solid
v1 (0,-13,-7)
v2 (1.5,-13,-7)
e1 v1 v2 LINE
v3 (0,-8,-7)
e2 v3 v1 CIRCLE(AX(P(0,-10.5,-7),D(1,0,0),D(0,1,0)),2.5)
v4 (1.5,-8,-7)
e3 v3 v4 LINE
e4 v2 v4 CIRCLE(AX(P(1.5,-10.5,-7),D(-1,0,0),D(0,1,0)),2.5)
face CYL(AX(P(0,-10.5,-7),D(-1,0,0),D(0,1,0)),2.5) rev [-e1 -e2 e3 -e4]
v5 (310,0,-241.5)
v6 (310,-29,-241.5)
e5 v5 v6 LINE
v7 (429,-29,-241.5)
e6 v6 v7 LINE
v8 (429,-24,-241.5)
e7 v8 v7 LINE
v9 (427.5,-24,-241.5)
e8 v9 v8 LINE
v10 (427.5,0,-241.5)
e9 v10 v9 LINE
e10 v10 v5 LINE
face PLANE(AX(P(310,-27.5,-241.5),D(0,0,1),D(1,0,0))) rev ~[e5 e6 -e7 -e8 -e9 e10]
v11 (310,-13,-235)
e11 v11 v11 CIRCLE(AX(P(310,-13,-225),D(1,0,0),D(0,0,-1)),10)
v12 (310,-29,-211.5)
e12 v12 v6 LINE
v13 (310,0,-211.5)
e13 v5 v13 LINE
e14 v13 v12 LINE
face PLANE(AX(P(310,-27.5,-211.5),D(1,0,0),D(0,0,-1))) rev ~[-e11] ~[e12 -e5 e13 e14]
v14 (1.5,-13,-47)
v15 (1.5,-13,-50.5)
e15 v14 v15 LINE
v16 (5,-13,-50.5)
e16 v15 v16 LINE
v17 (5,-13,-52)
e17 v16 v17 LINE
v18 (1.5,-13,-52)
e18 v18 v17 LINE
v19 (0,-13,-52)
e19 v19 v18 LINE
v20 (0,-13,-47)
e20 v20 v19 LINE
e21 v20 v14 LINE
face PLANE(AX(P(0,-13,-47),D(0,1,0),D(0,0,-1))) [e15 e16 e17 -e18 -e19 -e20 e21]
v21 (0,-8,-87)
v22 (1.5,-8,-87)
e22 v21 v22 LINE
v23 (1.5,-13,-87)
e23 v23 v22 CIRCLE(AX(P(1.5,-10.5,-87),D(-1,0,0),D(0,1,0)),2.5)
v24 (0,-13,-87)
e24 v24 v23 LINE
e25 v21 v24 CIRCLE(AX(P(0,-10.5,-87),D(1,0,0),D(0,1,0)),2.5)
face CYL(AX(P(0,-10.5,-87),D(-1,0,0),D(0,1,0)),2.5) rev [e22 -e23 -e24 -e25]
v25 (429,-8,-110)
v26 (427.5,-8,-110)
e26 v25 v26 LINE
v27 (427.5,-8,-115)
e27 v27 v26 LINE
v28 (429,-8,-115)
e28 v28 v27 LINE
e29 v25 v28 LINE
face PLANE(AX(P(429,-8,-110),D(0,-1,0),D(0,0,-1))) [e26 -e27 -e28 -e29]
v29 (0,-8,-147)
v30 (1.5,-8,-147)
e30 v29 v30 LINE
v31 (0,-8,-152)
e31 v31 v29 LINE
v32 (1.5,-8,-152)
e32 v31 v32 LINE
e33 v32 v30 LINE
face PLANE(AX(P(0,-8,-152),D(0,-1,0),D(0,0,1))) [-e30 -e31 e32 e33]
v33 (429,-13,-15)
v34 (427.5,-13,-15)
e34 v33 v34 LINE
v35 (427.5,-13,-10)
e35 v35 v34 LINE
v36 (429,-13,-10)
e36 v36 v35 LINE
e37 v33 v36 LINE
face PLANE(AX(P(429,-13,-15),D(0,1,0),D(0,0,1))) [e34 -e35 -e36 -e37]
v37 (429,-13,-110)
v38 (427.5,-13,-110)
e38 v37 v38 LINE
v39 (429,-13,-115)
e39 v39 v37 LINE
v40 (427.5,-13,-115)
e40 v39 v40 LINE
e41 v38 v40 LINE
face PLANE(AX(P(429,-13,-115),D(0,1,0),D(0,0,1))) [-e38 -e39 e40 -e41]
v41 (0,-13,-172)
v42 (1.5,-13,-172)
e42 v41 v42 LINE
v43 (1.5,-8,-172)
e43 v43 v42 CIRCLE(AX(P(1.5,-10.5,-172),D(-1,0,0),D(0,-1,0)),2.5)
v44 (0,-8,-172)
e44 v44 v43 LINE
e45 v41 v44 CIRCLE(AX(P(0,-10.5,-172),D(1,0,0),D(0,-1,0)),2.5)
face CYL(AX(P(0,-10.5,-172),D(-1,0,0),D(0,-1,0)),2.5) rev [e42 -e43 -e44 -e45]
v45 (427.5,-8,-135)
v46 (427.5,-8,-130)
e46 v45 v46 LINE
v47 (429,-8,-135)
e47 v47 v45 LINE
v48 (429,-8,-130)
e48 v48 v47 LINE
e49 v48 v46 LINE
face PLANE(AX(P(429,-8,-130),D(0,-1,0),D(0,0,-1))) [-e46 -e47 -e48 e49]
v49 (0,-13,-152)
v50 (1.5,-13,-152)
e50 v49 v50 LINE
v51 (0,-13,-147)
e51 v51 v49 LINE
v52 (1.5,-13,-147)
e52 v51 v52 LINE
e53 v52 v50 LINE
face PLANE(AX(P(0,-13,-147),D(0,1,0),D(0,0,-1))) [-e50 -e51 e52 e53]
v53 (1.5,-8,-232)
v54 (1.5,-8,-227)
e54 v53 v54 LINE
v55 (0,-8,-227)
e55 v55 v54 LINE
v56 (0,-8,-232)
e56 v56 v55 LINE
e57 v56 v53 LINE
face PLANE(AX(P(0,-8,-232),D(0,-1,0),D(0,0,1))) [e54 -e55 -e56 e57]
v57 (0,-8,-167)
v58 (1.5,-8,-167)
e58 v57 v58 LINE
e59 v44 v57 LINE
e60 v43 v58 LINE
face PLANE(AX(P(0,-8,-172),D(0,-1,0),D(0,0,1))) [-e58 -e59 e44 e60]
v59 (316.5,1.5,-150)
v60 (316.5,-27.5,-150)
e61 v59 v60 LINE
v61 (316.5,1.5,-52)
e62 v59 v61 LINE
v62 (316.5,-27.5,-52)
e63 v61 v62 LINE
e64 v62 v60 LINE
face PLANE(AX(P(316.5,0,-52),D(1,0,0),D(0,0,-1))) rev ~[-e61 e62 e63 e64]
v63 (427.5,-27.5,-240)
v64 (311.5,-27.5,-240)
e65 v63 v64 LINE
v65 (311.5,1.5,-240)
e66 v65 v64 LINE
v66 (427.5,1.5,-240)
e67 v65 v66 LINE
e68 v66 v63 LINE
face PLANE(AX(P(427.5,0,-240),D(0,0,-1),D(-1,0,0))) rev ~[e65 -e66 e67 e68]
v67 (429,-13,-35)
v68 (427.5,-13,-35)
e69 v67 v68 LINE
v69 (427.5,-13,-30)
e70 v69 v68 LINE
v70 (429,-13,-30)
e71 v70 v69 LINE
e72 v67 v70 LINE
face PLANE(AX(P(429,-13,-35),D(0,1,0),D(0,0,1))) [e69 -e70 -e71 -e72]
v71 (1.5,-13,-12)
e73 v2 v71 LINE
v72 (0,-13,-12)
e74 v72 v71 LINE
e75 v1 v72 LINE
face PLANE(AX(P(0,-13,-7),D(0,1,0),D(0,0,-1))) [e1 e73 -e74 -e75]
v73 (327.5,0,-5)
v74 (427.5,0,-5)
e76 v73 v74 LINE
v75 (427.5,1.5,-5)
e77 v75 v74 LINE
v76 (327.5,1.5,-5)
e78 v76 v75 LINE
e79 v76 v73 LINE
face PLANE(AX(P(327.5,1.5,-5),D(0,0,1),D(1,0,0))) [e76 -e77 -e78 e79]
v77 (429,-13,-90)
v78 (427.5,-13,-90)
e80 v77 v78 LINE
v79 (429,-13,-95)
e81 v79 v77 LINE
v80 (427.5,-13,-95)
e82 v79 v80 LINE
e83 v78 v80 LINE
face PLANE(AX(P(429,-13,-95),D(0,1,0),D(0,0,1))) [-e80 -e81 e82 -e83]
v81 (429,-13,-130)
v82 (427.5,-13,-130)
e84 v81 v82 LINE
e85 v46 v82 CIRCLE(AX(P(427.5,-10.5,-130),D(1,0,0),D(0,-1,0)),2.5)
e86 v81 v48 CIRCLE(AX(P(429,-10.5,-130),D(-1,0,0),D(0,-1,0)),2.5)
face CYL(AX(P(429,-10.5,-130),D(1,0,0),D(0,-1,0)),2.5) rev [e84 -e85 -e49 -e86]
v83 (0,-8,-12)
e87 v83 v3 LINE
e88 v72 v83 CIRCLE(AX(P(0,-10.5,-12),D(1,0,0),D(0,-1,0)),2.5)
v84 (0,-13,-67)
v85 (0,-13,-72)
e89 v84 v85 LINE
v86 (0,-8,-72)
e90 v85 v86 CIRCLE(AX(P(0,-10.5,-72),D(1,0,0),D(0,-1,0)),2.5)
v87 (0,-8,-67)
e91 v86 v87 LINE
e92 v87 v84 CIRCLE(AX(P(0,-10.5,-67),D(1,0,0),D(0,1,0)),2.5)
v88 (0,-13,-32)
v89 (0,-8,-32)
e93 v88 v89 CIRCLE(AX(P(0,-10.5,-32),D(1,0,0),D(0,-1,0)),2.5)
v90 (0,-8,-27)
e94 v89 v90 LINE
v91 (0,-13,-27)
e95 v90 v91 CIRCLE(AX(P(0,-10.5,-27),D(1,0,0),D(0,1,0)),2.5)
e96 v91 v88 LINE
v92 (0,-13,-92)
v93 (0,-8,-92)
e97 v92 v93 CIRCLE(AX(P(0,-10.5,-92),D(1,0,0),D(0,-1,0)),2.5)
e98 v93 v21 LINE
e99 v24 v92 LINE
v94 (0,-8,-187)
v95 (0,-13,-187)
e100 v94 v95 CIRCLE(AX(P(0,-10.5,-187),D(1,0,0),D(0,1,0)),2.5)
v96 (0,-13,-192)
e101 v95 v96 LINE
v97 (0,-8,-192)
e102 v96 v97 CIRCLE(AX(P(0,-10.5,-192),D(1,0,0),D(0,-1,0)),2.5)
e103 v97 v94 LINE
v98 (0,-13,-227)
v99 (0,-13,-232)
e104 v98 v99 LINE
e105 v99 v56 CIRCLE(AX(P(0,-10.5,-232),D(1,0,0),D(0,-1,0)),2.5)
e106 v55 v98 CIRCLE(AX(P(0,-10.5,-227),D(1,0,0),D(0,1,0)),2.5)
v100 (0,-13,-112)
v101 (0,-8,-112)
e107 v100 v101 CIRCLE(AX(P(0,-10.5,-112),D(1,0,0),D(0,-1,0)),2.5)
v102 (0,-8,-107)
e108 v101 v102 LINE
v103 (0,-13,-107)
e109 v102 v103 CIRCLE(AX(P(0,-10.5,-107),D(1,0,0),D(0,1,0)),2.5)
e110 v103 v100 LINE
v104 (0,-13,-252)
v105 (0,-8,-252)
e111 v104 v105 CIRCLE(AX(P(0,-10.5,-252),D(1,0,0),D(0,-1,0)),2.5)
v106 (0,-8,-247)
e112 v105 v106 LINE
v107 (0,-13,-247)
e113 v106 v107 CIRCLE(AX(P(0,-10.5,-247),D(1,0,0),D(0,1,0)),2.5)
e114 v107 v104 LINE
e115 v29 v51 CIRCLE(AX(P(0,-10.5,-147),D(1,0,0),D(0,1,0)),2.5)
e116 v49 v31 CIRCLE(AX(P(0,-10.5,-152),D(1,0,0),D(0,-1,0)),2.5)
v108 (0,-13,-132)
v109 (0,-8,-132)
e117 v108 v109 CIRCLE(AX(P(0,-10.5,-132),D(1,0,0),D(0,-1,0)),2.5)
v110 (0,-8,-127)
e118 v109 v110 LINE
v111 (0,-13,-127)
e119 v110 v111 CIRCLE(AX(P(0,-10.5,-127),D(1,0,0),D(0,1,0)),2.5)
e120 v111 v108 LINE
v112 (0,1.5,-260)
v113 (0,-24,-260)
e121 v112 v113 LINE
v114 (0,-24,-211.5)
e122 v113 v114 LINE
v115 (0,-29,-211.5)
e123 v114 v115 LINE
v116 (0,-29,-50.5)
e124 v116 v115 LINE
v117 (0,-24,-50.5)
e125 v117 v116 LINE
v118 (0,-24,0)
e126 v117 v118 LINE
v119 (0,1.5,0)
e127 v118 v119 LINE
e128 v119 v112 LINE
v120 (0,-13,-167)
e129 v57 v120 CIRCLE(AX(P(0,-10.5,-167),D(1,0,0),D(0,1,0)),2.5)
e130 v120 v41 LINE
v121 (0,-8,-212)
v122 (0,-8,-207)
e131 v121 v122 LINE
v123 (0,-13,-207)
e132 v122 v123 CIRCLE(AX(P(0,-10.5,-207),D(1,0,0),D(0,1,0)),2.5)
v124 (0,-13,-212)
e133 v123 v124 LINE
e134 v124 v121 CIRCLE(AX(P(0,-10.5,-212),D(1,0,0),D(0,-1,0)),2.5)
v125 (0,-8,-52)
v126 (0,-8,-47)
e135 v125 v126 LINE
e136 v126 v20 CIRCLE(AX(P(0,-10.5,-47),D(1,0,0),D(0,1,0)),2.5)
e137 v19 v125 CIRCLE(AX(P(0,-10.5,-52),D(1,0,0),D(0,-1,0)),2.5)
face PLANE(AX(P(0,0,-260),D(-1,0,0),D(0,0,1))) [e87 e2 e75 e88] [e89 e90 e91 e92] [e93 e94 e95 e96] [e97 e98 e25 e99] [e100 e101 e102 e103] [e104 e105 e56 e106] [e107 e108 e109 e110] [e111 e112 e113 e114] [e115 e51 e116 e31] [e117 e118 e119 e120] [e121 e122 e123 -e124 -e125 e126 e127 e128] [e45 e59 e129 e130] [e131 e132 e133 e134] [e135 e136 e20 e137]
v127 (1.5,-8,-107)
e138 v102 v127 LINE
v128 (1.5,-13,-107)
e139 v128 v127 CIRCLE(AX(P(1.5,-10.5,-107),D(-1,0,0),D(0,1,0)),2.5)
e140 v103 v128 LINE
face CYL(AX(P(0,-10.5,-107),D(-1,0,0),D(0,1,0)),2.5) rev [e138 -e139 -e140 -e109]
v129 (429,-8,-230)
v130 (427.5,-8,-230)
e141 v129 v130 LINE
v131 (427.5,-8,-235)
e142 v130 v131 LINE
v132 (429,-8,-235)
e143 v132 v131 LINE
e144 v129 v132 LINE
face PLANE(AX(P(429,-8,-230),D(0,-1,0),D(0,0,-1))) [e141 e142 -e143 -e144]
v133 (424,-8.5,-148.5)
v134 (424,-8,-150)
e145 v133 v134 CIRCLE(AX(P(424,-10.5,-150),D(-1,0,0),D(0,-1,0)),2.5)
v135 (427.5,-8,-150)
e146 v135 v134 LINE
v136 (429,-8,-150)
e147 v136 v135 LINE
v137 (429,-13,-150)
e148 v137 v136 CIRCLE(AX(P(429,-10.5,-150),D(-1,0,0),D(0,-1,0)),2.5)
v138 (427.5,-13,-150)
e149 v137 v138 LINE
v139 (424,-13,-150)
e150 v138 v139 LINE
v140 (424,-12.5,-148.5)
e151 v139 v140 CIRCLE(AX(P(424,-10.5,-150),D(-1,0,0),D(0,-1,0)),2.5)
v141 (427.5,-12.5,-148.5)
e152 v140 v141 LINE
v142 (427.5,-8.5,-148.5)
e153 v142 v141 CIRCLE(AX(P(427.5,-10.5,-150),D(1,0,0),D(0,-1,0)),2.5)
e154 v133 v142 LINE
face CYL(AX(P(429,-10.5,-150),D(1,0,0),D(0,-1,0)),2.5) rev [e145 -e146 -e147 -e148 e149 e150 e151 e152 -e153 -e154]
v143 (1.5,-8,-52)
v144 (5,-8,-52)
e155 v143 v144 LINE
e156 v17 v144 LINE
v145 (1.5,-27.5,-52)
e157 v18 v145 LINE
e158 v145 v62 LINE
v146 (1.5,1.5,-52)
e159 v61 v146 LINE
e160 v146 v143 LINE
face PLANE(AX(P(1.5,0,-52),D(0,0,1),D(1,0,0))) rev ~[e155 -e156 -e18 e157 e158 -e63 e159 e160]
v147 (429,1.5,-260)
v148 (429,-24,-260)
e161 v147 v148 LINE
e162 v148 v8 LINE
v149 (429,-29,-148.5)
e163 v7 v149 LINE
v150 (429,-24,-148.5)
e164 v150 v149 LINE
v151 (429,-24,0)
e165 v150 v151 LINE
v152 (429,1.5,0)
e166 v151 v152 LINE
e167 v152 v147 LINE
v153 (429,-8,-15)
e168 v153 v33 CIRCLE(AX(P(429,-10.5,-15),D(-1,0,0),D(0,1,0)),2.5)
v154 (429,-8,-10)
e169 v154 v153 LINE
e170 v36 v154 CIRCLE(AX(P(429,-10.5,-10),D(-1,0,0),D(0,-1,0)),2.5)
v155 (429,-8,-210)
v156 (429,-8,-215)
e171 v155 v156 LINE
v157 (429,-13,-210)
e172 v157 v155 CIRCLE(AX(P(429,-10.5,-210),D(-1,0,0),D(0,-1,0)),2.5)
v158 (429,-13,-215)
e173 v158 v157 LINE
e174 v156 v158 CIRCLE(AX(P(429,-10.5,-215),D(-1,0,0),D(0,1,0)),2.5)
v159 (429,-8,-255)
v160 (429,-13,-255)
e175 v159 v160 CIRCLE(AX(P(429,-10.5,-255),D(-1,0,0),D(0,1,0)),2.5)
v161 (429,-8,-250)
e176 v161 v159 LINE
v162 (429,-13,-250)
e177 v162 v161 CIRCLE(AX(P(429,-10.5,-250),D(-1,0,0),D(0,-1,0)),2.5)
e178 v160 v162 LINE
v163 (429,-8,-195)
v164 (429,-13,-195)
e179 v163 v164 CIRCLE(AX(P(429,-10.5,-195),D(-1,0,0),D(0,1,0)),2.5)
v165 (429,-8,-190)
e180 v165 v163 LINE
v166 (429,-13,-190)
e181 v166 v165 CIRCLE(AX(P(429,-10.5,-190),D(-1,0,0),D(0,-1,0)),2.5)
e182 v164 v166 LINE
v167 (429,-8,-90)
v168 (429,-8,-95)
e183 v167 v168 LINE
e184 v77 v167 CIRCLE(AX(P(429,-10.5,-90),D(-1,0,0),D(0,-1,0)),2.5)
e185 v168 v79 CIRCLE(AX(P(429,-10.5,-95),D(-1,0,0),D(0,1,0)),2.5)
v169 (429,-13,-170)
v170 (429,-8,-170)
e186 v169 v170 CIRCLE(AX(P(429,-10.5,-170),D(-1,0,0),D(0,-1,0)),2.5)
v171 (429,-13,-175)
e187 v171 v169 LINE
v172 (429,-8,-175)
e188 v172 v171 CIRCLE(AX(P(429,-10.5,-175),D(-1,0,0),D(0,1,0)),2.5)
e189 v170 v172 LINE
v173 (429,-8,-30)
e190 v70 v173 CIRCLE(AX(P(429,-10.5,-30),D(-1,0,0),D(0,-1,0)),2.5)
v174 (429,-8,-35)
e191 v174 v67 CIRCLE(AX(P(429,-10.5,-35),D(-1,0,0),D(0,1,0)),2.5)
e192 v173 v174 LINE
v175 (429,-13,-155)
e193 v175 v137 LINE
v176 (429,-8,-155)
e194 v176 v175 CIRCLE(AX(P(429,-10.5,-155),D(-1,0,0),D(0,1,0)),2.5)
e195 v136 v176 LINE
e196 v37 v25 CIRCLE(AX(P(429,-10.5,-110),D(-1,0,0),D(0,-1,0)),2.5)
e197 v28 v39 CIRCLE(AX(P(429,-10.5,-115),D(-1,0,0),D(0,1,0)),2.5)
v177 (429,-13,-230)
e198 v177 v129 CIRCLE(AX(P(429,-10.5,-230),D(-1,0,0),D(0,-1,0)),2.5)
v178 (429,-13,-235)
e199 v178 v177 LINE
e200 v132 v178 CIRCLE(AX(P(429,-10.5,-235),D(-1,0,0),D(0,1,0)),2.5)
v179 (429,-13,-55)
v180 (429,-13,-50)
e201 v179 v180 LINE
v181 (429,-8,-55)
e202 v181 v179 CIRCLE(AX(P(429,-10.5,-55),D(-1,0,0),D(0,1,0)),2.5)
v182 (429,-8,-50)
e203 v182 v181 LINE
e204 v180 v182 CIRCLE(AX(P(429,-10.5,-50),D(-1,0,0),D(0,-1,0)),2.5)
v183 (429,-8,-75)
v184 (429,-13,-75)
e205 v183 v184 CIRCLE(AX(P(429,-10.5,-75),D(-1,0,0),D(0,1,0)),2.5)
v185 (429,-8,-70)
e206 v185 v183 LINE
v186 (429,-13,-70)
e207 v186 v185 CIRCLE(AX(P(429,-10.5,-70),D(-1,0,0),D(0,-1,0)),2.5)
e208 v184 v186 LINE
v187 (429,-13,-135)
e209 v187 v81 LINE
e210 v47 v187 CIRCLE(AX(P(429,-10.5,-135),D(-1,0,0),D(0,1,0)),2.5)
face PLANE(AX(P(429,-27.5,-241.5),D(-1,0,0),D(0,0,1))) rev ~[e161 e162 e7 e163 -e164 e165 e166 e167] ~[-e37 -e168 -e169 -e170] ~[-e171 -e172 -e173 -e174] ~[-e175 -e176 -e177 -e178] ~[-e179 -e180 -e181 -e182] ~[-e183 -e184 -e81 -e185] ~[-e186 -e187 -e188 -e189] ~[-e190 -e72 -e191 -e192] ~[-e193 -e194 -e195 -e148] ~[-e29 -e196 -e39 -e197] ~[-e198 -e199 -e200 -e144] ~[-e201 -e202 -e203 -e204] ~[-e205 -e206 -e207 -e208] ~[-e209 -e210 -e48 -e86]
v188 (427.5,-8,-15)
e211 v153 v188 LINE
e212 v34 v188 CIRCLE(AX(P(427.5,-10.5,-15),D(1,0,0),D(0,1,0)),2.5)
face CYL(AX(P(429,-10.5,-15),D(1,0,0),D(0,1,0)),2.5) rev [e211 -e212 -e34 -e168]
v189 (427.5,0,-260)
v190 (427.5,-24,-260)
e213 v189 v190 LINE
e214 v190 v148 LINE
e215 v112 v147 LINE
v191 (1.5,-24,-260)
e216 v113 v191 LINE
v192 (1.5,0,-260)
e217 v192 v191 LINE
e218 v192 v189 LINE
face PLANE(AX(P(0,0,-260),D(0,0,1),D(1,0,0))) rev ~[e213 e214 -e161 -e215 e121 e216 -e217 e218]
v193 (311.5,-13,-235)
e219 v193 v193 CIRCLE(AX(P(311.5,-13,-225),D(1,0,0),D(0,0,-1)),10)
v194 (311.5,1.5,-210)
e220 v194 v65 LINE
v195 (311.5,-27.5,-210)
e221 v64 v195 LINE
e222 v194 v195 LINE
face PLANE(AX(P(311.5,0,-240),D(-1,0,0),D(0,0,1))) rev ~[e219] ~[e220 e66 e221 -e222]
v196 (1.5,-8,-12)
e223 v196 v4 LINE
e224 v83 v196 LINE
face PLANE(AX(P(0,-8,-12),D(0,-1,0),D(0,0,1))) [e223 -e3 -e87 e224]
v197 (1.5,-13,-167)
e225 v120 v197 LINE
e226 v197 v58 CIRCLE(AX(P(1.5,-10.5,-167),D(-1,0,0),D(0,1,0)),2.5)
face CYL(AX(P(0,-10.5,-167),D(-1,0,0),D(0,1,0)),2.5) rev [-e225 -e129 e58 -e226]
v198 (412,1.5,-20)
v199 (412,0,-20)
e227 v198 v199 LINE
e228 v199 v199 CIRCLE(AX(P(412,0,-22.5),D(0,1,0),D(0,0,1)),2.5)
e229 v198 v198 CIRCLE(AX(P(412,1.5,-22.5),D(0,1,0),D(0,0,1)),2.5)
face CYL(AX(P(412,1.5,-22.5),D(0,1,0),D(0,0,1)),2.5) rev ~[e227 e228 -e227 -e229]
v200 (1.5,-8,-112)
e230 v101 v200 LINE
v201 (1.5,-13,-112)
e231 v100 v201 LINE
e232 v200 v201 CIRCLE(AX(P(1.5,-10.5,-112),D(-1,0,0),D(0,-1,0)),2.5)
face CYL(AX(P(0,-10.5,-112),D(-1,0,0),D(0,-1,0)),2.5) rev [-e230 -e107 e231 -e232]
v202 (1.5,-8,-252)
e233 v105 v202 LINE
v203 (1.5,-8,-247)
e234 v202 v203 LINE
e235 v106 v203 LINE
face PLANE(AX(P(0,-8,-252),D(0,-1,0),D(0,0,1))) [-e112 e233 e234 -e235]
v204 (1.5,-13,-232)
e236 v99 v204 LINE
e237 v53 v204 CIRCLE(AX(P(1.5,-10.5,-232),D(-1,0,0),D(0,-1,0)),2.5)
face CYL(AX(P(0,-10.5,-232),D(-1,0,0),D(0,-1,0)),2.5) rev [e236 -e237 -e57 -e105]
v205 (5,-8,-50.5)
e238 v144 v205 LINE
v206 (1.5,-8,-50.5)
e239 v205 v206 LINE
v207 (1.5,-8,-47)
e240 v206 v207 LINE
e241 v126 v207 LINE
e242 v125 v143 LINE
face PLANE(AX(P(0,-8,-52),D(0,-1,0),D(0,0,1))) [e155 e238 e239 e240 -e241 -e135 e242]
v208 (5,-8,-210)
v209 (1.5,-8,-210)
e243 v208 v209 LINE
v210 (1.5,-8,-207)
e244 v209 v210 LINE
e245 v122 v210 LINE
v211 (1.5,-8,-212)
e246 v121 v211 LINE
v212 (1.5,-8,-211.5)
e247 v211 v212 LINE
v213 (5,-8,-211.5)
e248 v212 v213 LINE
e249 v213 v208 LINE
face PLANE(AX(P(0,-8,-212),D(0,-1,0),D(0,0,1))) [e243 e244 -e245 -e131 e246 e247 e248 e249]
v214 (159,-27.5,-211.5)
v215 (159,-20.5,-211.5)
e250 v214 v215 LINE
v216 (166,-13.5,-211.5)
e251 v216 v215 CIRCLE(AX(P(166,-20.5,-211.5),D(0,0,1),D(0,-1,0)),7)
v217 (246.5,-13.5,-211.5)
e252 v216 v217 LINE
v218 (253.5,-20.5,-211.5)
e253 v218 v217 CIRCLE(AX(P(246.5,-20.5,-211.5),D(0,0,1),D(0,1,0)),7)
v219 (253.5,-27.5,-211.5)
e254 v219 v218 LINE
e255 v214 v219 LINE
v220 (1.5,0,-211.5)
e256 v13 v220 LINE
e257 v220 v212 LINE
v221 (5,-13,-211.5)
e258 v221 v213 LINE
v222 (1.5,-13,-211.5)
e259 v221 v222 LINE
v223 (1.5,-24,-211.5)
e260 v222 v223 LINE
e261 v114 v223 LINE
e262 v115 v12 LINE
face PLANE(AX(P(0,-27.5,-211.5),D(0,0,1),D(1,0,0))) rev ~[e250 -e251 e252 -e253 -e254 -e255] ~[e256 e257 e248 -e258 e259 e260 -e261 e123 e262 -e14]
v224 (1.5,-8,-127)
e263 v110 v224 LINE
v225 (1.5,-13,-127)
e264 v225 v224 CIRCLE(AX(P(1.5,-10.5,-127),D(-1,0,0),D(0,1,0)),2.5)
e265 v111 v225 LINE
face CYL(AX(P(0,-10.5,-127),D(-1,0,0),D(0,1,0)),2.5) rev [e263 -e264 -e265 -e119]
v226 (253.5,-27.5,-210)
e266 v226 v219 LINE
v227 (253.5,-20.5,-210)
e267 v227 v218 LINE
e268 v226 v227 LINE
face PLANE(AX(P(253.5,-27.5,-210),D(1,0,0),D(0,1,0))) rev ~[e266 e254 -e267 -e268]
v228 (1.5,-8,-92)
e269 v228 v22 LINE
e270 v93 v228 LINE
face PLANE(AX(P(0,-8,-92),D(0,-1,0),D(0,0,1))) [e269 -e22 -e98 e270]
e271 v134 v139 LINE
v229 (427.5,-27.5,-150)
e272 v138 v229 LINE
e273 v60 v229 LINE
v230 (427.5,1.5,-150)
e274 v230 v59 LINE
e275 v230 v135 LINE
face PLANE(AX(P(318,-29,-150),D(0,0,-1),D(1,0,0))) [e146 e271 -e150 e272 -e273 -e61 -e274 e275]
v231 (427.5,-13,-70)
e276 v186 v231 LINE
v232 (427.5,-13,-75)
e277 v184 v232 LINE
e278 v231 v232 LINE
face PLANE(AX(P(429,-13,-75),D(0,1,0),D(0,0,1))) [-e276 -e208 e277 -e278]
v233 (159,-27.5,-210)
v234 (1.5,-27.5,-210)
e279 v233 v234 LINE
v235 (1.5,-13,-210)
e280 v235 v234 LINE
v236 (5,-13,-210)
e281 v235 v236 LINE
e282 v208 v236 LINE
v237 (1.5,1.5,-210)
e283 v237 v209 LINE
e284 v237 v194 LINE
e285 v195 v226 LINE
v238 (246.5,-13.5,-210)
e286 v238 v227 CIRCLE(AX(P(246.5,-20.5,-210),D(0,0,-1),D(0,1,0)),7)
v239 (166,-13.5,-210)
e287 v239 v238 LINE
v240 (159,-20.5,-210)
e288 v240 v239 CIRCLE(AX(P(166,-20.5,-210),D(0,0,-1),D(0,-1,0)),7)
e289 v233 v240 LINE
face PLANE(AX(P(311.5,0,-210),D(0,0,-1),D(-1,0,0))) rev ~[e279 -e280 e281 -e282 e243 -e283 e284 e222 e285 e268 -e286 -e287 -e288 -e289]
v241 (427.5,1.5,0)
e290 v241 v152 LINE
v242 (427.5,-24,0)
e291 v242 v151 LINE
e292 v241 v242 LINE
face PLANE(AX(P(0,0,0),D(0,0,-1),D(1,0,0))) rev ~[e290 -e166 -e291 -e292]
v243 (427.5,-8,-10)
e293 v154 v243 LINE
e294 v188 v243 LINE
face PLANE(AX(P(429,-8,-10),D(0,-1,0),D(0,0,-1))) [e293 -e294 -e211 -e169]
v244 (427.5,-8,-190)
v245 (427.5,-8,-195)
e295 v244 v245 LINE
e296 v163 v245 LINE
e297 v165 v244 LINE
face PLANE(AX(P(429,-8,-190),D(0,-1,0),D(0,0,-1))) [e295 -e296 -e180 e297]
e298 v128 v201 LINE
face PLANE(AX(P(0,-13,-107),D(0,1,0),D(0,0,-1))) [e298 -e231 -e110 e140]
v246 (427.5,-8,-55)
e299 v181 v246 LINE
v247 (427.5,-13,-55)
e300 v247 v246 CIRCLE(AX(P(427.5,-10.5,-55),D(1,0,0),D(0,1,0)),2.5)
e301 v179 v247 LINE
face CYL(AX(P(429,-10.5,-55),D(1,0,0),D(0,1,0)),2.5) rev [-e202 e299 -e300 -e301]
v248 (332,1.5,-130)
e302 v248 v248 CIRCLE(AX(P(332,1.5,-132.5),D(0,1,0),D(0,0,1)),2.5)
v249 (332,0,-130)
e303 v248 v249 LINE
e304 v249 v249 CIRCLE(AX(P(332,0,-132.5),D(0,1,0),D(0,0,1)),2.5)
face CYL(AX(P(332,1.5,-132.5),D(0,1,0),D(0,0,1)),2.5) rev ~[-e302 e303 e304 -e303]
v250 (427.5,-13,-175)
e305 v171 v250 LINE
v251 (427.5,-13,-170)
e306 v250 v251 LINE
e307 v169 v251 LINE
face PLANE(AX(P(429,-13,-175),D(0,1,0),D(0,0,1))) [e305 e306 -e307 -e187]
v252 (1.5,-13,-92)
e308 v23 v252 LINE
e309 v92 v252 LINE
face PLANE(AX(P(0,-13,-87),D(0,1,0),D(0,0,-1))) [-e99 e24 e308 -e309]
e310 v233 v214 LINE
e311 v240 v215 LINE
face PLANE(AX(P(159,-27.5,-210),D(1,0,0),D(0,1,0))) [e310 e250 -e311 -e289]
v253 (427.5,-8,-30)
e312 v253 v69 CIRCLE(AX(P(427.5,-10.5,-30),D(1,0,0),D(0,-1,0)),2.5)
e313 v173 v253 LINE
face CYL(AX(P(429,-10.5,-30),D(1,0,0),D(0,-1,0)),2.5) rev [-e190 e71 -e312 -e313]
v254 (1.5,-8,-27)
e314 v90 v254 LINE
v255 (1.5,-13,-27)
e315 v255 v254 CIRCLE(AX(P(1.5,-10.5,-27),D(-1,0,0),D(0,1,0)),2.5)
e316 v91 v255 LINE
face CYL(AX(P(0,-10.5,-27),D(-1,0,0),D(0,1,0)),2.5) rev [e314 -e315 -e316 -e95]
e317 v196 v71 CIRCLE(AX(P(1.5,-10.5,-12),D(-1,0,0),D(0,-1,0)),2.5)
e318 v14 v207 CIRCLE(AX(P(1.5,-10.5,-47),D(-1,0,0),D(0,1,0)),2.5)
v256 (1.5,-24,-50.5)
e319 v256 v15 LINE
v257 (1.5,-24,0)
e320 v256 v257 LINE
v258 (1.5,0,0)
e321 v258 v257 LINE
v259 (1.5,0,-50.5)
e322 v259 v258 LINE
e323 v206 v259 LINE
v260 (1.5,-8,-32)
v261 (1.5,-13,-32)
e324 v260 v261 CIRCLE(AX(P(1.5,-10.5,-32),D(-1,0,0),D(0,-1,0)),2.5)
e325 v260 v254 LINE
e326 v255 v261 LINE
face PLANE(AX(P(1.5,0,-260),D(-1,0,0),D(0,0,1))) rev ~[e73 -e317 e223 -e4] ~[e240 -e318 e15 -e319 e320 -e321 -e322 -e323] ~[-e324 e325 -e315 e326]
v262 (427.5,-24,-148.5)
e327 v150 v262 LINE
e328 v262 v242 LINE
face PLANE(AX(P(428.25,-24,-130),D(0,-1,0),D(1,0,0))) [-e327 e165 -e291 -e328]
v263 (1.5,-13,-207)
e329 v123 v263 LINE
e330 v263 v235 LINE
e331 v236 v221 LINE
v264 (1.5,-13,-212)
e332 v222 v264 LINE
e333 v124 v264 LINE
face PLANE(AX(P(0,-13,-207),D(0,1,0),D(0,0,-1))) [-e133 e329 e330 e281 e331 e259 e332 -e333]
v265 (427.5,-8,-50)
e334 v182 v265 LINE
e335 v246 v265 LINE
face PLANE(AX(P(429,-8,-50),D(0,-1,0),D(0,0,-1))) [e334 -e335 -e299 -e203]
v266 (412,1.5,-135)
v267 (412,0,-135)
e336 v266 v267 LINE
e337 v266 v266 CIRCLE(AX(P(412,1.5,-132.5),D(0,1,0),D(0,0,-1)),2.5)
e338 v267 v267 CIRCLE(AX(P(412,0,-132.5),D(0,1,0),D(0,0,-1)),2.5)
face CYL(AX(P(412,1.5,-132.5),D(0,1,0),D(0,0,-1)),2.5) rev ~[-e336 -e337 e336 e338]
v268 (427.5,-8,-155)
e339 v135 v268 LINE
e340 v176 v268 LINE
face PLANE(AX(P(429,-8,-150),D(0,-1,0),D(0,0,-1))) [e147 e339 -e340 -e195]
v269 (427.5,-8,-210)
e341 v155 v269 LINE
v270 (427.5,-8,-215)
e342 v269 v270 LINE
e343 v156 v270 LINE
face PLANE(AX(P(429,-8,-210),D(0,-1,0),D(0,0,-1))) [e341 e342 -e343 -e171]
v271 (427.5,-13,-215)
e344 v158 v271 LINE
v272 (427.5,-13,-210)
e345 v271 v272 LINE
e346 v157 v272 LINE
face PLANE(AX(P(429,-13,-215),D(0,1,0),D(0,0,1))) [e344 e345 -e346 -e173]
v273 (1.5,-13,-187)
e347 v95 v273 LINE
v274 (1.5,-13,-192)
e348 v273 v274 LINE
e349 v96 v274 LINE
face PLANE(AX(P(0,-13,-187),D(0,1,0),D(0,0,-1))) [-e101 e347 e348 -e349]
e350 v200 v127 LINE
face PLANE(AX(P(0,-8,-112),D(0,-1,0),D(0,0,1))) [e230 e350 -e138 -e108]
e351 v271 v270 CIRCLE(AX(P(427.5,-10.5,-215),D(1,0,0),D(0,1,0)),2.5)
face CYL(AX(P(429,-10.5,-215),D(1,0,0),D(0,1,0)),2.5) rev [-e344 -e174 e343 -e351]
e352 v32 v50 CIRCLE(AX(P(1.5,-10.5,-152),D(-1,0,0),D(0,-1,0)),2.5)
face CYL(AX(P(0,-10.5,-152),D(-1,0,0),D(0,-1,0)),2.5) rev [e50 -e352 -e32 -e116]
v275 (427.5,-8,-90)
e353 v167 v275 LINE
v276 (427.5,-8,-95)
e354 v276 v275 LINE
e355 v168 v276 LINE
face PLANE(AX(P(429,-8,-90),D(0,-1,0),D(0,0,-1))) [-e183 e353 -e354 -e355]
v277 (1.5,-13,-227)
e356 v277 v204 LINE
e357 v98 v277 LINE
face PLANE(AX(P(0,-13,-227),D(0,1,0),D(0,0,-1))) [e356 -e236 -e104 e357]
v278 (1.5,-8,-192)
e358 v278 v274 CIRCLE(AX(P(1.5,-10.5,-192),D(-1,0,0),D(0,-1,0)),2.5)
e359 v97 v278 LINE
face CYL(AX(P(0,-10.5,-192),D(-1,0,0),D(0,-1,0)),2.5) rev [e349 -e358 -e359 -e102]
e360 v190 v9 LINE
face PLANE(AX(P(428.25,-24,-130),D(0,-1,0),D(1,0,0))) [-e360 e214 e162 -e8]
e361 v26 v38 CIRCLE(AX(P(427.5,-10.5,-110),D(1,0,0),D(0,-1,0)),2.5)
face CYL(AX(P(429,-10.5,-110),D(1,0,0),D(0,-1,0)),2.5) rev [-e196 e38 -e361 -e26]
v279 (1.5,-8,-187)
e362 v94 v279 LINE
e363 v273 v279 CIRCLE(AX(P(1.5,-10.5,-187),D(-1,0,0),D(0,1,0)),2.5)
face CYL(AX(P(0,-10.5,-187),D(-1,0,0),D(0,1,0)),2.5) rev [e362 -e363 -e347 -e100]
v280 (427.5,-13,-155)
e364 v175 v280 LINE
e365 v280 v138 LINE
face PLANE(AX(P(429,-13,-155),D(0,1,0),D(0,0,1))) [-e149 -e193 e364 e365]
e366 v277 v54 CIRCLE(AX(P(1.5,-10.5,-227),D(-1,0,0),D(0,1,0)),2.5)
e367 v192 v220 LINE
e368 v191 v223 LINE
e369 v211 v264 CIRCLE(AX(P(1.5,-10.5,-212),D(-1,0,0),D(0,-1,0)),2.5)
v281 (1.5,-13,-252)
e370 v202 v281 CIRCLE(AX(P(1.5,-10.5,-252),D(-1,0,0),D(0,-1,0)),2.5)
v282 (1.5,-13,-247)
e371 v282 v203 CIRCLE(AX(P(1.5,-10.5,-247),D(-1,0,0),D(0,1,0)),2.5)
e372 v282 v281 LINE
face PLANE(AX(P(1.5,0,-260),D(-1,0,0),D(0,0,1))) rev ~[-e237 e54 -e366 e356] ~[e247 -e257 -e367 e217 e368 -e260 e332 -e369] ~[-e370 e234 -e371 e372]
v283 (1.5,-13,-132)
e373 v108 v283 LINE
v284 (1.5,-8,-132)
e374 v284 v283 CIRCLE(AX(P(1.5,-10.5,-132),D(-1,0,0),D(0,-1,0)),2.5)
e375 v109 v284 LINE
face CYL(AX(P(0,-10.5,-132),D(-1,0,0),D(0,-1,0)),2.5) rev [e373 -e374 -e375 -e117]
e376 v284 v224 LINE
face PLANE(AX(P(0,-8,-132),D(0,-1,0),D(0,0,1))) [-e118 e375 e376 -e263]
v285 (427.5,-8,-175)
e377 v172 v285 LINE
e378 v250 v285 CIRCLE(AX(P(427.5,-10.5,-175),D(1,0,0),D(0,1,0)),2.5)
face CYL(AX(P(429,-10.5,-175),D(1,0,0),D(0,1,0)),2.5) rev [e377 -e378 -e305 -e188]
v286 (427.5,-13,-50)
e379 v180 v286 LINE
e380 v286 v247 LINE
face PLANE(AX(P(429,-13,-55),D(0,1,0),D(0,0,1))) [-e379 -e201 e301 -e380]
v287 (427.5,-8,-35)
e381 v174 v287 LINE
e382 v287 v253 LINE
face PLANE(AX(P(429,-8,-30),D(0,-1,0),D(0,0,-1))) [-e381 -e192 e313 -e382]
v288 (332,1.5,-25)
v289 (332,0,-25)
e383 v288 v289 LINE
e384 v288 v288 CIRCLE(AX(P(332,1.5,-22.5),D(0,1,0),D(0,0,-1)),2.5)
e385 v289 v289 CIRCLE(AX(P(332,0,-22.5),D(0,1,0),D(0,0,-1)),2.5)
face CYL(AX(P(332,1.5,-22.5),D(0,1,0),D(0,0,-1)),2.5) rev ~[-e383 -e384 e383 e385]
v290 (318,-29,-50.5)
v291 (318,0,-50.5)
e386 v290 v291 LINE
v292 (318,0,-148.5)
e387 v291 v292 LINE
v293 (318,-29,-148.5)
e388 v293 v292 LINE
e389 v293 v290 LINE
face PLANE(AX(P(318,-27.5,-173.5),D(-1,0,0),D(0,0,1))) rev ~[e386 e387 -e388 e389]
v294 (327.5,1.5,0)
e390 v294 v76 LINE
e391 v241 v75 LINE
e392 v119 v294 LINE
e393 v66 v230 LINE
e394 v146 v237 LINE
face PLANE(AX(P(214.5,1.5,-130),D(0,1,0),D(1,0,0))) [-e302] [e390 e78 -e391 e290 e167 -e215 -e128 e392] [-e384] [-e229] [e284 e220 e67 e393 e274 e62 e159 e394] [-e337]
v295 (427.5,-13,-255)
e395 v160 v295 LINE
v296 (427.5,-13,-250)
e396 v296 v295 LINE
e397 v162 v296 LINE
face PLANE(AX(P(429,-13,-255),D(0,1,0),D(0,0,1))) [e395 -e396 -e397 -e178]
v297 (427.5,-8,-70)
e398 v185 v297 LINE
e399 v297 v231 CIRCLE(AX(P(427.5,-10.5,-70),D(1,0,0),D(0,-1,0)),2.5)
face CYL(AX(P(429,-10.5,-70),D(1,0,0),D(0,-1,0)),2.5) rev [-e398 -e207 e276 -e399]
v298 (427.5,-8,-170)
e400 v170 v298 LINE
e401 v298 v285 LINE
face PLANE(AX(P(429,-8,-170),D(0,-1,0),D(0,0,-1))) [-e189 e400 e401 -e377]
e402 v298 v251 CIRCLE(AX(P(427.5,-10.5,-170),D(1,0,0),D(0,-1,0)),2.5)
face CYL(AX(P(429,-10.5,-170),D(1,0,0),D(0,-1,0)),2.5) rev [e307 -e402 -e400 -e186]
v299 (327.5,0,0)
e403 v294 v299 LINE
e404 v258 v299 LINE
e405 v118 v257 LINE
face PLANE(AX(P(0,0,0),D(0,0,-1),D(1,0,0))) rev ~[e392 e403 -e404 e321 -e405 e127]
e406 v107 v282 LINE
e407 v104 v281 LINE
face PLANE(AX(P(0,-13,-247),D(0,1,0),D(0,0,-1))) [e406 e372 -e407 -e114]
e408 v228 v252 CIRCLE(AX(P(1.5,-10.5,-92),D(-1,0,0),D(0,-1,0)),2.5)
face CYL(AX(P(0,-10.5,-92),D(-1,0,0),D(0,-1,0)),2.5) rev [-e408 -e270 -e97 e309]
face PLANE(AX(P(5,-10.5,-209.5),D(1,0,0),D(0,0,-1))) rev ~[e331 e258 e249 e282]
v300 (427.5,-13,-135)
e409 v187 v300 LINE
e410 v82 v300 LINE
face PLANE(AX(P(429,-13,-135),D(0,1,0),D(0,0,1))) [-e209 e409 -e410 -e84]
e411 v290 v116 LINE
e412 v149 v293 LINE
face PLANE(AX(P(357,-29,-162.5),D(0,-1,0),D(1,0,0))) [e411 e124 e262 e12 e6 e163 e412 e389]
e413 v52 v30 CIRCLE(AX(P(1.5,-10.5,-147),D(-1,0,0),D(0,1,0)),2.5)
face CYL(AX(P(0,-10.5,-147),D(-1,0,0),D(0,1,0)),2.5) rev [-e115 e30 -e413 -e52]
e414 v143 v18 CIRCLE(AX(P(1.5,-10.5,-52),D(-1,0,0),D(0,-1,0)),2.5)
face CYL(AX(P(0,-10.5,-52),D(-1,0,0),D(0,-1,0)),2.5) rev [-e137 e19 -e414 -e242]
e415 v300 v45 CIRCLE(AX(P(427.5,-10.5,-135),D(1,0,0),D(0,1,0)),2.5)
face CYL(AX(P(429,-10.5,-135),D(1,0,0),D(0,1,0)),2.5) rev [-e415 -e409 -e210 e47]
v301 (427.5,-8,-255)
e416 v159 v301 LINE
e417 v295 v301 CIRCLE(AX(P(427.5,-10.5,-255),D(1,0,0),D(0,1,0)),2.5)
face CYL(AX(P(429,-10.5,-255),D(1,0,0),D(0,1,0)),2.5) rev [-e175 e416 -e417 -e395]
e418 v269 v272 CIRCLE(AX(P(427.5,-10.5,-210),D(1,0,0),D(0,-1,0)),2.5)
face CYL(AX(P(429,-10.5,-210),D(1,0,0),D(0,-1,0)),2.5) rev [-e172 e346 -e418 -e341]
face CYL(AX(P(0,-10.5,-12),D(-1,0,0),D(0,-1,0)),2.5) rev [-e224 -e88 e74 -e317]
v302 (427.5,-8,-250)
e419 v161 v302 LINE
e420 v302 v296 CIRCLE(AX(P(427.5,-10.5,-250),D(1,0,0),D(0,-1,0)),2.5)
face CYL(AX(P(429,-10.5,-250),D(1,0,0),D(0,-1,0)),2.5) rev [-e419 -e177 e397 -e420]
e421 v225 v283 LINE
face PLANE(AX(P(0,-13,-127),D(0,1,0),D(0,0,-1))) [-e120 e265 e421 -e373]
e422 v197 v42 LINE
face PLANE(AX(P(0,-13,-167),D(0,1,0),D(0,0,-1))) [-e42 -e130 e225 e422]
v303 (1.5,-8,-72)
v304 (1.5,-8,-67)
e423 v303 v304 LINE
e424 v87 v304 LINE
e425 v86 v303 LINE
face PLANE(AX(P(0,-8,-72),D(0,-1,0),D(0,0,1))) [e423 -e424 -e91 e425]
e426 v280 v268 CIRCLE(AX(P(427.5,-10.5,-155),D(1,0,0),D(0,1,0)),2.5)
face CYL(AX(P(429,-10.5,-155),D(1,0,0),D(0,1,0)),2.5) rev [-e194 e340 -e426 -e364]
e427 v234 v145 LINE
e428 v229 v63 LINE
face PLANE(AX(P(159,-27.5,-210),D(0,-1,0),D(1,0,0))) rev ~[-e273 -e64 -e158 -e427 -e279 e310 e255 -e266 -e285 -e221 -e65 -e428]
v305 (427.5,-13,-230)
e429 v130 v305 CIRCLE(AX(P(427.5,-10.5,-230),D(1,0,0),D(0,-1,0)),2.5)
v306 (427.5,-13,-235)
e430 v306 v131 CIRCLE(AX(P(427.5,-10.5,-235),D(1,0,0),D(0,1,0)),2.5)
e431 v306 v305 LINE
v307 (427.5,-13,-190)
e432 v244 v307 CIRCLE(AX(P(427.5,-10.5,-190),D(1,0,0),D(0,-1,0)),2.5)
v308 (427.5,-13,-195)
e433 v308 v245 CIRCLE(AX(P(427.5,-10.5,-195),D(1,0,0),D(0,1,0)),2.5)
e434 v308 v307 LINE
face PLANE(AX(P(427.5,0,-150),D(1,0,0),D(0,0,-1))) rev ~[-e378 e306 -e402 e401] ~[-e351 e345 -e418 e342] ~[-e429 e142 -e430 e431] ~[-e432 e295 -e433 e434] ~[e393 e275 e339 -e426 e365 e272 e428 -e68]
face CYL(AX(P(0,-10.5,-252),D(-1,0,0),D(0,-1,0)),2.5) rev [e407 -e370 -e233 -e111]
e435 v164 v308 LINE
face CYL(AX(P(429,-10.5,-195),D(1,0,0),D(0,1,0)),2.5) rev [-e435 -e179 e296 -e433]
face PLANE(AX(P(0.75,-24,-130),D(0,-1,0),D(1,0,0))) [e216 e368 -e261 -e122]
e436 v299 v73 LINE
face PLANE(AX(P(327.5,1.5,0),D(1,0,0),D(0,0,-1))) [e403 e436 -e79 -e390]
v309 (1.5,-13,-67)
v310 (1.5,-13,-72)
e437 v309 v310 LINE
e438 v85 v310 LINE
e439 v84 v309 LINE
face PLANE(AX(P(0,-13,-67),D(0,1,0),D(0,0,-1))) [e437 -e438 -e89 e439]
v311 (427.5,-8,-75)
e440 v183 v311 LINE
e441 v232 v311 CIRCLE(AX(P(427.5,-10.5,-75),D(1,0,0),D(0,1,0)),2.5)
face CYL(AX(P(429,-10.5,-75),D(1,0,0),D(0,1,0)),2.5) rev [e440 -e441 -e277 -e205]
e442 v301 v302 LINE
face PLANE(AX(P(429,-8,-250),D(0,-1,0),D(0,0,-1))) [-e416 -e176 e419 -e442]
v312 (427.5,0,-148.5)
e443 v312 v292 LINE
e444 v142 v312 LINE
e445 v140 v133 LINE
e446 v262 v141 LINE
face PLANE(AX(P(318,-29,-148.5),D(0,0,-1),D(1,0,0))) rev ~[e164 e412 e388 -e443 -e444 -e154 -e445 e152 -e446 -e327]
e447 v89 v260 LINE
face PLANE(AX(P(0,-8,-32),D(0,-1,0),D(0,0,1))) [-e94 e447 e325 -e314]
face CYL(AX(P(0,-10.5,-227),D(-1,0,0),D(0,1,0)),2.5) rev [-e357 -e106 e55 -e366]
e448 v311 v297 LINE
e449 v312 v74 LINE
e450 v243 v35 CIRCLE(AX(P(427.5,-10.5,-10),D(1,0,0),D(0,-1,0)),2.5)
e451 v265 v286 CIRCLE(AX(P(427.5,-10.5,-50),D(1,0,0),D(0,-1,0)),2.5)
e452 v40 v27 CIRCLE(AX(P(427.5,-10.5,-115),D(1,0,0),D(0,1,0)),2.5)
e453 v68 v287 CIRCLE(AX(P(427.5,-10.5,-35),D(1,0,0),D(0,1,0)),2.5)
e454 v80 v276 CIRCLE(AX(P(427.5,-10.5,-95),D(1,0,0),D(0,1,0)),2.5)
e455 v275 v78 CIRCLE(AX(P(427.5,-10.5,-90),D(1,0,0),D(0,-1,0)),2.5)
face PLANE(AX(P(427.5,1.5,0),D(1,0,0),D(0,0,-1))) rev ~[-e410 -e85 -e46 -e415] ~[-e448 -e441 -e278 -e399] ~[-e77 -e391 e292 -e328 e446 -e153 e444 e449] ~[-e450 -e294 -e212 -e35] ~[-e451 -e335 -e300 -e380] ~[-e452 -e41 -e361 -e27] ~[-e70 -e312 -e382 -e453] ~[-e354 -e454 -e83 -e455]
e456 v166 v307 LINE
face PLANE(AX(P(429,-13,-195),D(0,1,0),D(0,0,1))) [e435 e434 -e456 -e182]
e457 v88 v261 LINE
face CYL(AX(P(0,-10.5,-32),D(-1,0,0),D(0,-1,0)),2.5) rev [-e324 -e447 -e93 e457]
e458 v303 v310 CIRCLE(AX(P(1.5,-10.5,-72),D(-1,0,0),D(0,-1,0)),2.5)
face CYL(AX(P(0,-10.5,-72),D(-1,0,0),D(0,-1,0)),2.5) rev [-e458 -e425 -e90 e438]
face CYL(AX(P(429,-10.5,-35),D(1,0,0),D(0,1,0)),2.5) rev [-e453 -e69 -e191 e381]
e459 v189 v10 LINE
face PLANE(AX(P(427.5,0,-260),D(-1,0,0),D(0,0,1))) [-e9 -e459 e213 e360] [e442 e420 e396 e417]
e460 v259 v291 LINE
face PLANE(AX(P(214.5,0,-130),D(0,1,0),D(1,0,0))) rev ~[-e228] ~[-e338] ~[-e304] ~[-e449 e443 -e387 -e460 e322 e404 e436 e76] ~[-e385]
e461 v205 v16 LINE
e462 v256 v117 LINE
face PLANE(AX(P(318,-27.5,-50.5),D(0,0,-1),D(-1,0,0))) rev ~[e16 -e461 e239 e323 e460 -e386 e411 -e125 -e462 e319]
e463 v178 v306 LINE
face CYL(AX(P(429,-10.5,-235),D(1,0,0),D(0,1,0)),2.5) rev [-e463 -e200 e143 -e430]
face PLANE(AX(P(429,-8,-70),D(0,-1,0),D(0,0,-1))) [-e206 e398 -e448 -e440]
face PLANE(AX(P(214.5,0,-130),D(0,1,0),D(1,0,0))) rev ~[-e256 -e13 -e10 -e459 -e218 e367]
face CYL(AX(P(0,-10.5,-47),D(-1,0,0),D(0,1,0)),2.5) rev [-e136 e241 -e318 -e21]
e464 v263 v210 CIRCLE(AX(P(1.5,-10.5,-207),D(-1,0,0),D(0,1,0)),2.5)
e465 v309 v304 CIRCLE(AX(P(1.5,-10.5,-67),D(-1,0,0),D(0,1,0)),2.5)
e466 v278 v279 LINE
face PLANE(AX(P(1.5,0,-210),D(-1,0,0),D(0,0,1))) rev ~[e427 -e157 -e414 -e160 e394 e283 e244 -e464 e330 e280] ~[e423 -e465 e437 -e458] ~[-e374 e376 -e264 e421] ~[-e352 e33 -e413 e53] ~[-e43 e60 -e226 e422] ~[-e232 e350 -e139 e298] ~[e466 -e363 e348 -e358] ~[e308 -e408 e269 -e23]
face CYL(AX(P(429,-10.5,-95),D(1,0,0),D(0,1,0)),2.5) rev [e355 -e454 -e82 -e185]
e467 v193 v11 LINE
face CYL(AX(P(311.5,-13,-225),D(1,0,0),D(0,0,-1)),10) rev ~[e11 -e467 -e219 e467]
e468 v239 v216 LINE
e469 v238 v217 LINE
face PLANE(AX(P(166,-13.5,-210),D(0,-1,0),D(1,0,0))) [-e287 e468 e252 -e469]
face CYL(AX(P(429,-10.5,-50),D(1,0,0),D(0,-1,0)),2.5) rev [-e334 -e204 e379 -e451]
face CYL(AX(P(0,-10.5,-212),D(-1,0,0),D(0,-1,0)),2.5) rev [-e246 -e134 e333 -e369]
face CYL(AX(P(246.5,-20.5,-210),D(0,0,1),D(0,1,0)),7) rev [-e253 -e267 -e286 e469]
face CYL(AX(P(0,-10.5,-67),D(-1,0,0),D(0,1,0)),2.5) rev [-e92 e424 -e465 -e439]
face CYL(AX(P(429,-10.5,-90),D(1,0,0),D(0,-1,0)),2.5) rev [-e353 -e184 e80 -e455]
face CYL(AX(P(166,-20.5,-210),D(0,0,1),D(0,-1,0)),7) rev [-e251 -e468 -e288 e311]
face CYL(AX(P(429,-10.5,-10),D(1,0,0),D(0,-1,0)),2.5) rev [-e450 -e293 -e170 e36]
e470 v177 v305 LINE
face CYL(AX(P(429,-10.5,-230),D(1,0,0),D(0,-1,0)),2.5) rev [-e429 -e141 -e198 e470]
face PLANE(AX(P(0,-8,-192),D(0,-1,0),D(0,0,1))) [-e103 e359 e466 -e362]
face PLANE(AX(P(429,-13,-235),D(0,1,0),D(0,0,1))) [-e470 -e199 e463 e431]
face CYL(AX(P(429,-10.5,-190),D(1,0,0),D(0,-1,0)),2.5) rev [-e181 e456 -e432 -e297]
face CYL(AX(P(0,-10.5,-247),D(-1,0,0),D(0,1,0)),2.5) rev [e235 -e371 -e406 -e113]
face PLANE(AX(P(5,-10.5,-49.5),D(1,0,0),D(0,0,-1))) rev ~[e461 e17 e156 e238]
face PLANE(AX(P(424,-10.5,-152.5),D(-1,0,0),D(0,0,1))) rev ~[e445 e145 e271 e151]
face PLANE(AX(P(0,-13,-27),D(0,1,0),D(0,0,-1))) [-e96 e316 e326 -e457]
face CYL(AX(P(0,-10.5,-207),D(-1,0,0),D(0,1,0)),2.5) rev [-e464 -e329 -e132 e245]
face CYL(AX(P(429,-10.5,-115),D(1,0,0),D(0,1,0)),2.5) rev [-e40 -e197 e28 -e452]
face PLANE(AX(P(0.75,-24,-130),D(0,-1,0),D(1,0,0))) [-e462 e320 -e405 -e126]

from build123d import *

# Parameters (mm, degrees)
SKETCH_1_W             = 429
SKETCH_1_H             = 260
EXTRUDE_1_DEPTH        = 1.5
CUT_EXTRUDE_1_DEPTH    = 1.5
EXTRUDE_6_DEPTH        = 27.5
EXTRUDE_7_DEPTH        = 1.5
SKETCH_10_W            = 1.5
SKETCH_10_H            = 260
EXTRUDE_8_DEPTH        = 24
CUT_EXTRUDE_2_DEPTH    = 5
CUT_EXTRUDE_3_DEPTH    = 5
PATTERN_LINEAR_1_COUNT = 13
PATTERN_LINEAR_1_PITCH = 20
PATTERN_LINEAR_2_COUNT = 13
PATTERN_LINEAR_2_PITCH = 20
SKETCH_13_W            = 100
SKETCH_13_H            = 5
CUT_EXTRUDE_4_DEPTH    = 5
SKETCH_19_R            = 10
CUT_EXTRUDE_9_DEPTH    = 1.5
CUT_EXTRUDE_10_DEPTH   = 10
SKETCH_21_W            = 81
SKETCH_21_H            = 25
CUT_EXTRUDE_11_DEPTH   = 503.564672455
SKETCH_22_W            = 78
SKETCH_22_H            = 1.5
EXTRUDE_10_DEPTH       = 29
SKETCH_23_W            = 81
SKETCH_23_H            = 25
EXTRUDE_11_DEPTH       = 1.5
SKETCH_24_R            = 2.5
CUT_EXTRUDE_12_DEPTH   = 1.5
SKETCH_25_W            = 94.5
SKETCH_25_H            = 7
CUT_EXTRUDE_13_DEPTH   = 10


with BuildPart() as part:
    # 草图1 → 凸台-拉伸1 (new body)
    with BuildSketch(Plane(origin=(0, 0, 0), x_dir=(1, 0, 0), z_dir=(0, 1, 0))):
        with Locations((214.5, 130)):
            Rectangle(SKETCH_1_W, SKETCH_1_H)
    extrude(amount=EXTRUDE_1_DEPTH)

    # 草图2 → 切除-拉伸1 (cut)
    with BuildSketch(Plane(origin=(0, 1.5, 0), x_dir=(1, 0, 0), z_dir=(0, 1, 0))):
        Polygon((311.5, 210), (311.5, 240), (427.5, 240), (427.5, 150), (397.5, 150), (397.5, 175), (316.5, 175), (316.5, 52), (1.5, 52), (1.5, 210), align=None)
    extrude(amount=-CUT_EXTRUDE_1_DEPTH, mode=Mode.SUBTRACT)

    # 草图7 → 凸台-拉伸6 (add)
    with BuildSketch(Plane.XZ):
        Polygon((0, -50.5), (318, -50.5), (318, -173.5), (396, -173.5), (396, -148.5), (429, -148.5), (429, -241.5), (310, -241.5), (310, -211.5), (0, -211.5), align=None)
        Polygon((1.5, -52), (316.5, -52), (316.5, -175), (397.5, -175), (397.5, -150), (427.5, -150), (427.5, -240), (311.5, -240), (311.5, -210), (1.5, -210), align=None, mode=Mode.SUBTRACT)
    extrude(amount=EXTRUDE_6_DEPTH)

    # 草图9 → 凸台-拉伸7 (add)
    with BuildSketch(Plane.XZ.offset(27.5)):
        Polygon((318, -50.5), (0, -50.5), (0, -211.5), (310, -211.5), (310, -241.5), (429, -241.5), (429, -148.5), (396, -148.5), (396, -173.5), (318, -173.5), align=None)
    extrude(amount=EXTRUDE_7_DEPTH)

    # 草图10 → 凸台-拉伸8 (add)
    with BuildSketch(Plane.XZ):
        with Locations((0.75, -130)):
            Rectangle(SKETCH_10_W, SKETCH_10_H)
        with Locations((428.25, -130)):
            Rectangle(SKETCH_10_W, SKETCH_10_H)
    extrude(amount=EXTRUDE_8_DEPTH)

    # 草图11 → 切除-拉伸2 (cut)
    with BuildSketch(Plane.ZY):
        with BuildLine():
            Line((-252, -8), (-247, -8))
            ThreePointArc((-247, -8), (-244.5, -10.5), (-247, -13))
            Line((-247, -13), (-252, -13))
            ThreePointArc((-252, -13), (-254.5, -10.5), (-252, -8))
        make_face()
    cut_extrude_2 = extrude(amount=-CUT_EXTRUDE_2_DEPTH, mode=Mode.SUBTRACT)

    # 草图12 → 切除-拉伸3 (cut)
    with BuildSketch(Plane(origin=(429, 0, 0), x_dir=(0, 0, -1), z_dir=(1, 0, 0))):
        with BuildLine():
            Line((250, -8), (255, -8))
            ThreePointArc((255, -8), (257.5, -10.5), (255, -13))
            Line((255, -13), (250, -13))
            ThreePointArc((250, -13), (247.5, -10.5), (250, -8))
        make_face()
    cut_extrude_3 = extrude(amount=-CUT_EXTRUDE_3_DEPTH, mode=Mode.SUBTRACT)

    # 阵列(线性)1: 切除-拉伸2 ×13
    with Locations(*[(0, 0, i * PATTERN_LINEAR_1_PITCH) for i in range(1, PATTERN_LINEAR_1_COUNT)]):
        add(cut_extrude_2, mode=Mode.SUBTRACT)

    # 阵列(线性)2: 切除-拉伸3 ×13
    with Locations(*[(0, 0, i * PATTERN_LINEAR_2_PITCH) for i in range(1, PATTERN_LINEAR_2_COUNT)]):
        add(cut_extrude_3, mode=Mode.SUBTRACT)

    # 草图13 → 切除-拉伸4 (cut)
    with BuildSketch(Plane(origin=(0, 1.5, 0), x_dir=(1, 0, 0), z_dir=(0, 1, 0))):
        with Locations((377.5, 2.5)):
            Rectangle(SKETCH_13_W, SKETCH_13_H)
    extrude(amount=-CUT_EXTRUDE_4_DEPTH, mode=Mode.SUBTRACT)

    # 草图19 → 切除-拉伸9 (cut)
    with BuildSketch(Plane(origin=(311.5, 0, 0), x_dir=(0, 0, -1), z_dir=(1, 0, 0))):
        with Locations((225, -13)):
            Circle(SKETCH_19_R)
    extrude(amount=-CUT_EXTRUDE_9_DEPTH, mode=Mode.SUBTRACT)

    # 草图20 → 切除-拉伸10 (cut)
    with BuildSketch(Plane.XY.offset(-210)):
        with BuildLine():
            Line((246.5, -27.5), (166, -27.5))
            ThreePointArc((166, -27.5), (159, -20.5), (166, -13.5))
            Line((166, -13.5), (246.5, -13.5))
            ThreePointArc((246.5, -13.5), (253.5, -20.5), (246.5, -27.5))
        make_face()
    extrude(amount=-CUT_EXTRUDE_10_DEPTH, mode=Mode.SUBTRACT)

    # 草图21 → 切除-拉伸11 (cut, through all)
    with BuildSketch(Plane(origin=(0, 1.5, 0), x_dir=(1, 0, 0), z_dir=(0, 1, 0))):
        with Locations((357, 162.5)):
            Rectangle(SKETCH_21_W, SKETCH_21_H)
    extrude(amount=-CUT_EXTRUDE_11_DEPTH, mode=Mode.SUBTRACT)

    # 草图22 → 凸台-拉伸10 (add)
    with BuildSketch(Plane.XZ.offset(29)):
        with Locations((357, -149.25)):
            Rectangle(SKETCH_22_W, SKETCH_22_H)
    extrude(amount=-EXTRUDE_10_DEPTH)

    # 草图23 → 凸台-拉伸11 (add)
    with BuildSketch(Plane.XZ.offset(29)):
        with Locations((357, -162.5)):
            Rectangle(SKETCH_23_W, SKETCH_23_H)
    extrude(amount=-EXTRUDE_11_DEPTH)

    # 草图24 → 切除-拉伸12 (cut)
    with BuildSketch(Plane(origin=(0, 1.5, 0), x_dir=(1, 0, 0), z_dir=(0, 1, 0))):
        with Locations(Location((332, 132.5, 0), (0, 0, 270))):
            Circle(SKETCH_24_R)
        with Locations(Location((412, 132.5, 0), (0, 0, 90))):
            Circle(SKETCH_24_R)
        with Locations(Location((412, 22.5, 0), (0, 0, 270))):
            Circle(SKETCH_24_R)
        with Locations(Location((332, 22.5, 0), (0, 0, 90))):
            Circle(SKETCH_24_R)
    extrude(amount=-CUT_EXTRUDE_12_DEPTH, mode=Mode.SUBTRACT)

    # 草图25 → 切除-拉伸13 (cut)
    with BuildSketch(Plane.XY.offset(-210)):
        with Locations((206.25, -24)):
            Rectangle(SKETCH_25_W, SKETCH_25_H)
    extrude(amount=-CUT_EXTRUDE_13_DEPTH, mode=Mode.SUBTRACT)


solid = part.part
